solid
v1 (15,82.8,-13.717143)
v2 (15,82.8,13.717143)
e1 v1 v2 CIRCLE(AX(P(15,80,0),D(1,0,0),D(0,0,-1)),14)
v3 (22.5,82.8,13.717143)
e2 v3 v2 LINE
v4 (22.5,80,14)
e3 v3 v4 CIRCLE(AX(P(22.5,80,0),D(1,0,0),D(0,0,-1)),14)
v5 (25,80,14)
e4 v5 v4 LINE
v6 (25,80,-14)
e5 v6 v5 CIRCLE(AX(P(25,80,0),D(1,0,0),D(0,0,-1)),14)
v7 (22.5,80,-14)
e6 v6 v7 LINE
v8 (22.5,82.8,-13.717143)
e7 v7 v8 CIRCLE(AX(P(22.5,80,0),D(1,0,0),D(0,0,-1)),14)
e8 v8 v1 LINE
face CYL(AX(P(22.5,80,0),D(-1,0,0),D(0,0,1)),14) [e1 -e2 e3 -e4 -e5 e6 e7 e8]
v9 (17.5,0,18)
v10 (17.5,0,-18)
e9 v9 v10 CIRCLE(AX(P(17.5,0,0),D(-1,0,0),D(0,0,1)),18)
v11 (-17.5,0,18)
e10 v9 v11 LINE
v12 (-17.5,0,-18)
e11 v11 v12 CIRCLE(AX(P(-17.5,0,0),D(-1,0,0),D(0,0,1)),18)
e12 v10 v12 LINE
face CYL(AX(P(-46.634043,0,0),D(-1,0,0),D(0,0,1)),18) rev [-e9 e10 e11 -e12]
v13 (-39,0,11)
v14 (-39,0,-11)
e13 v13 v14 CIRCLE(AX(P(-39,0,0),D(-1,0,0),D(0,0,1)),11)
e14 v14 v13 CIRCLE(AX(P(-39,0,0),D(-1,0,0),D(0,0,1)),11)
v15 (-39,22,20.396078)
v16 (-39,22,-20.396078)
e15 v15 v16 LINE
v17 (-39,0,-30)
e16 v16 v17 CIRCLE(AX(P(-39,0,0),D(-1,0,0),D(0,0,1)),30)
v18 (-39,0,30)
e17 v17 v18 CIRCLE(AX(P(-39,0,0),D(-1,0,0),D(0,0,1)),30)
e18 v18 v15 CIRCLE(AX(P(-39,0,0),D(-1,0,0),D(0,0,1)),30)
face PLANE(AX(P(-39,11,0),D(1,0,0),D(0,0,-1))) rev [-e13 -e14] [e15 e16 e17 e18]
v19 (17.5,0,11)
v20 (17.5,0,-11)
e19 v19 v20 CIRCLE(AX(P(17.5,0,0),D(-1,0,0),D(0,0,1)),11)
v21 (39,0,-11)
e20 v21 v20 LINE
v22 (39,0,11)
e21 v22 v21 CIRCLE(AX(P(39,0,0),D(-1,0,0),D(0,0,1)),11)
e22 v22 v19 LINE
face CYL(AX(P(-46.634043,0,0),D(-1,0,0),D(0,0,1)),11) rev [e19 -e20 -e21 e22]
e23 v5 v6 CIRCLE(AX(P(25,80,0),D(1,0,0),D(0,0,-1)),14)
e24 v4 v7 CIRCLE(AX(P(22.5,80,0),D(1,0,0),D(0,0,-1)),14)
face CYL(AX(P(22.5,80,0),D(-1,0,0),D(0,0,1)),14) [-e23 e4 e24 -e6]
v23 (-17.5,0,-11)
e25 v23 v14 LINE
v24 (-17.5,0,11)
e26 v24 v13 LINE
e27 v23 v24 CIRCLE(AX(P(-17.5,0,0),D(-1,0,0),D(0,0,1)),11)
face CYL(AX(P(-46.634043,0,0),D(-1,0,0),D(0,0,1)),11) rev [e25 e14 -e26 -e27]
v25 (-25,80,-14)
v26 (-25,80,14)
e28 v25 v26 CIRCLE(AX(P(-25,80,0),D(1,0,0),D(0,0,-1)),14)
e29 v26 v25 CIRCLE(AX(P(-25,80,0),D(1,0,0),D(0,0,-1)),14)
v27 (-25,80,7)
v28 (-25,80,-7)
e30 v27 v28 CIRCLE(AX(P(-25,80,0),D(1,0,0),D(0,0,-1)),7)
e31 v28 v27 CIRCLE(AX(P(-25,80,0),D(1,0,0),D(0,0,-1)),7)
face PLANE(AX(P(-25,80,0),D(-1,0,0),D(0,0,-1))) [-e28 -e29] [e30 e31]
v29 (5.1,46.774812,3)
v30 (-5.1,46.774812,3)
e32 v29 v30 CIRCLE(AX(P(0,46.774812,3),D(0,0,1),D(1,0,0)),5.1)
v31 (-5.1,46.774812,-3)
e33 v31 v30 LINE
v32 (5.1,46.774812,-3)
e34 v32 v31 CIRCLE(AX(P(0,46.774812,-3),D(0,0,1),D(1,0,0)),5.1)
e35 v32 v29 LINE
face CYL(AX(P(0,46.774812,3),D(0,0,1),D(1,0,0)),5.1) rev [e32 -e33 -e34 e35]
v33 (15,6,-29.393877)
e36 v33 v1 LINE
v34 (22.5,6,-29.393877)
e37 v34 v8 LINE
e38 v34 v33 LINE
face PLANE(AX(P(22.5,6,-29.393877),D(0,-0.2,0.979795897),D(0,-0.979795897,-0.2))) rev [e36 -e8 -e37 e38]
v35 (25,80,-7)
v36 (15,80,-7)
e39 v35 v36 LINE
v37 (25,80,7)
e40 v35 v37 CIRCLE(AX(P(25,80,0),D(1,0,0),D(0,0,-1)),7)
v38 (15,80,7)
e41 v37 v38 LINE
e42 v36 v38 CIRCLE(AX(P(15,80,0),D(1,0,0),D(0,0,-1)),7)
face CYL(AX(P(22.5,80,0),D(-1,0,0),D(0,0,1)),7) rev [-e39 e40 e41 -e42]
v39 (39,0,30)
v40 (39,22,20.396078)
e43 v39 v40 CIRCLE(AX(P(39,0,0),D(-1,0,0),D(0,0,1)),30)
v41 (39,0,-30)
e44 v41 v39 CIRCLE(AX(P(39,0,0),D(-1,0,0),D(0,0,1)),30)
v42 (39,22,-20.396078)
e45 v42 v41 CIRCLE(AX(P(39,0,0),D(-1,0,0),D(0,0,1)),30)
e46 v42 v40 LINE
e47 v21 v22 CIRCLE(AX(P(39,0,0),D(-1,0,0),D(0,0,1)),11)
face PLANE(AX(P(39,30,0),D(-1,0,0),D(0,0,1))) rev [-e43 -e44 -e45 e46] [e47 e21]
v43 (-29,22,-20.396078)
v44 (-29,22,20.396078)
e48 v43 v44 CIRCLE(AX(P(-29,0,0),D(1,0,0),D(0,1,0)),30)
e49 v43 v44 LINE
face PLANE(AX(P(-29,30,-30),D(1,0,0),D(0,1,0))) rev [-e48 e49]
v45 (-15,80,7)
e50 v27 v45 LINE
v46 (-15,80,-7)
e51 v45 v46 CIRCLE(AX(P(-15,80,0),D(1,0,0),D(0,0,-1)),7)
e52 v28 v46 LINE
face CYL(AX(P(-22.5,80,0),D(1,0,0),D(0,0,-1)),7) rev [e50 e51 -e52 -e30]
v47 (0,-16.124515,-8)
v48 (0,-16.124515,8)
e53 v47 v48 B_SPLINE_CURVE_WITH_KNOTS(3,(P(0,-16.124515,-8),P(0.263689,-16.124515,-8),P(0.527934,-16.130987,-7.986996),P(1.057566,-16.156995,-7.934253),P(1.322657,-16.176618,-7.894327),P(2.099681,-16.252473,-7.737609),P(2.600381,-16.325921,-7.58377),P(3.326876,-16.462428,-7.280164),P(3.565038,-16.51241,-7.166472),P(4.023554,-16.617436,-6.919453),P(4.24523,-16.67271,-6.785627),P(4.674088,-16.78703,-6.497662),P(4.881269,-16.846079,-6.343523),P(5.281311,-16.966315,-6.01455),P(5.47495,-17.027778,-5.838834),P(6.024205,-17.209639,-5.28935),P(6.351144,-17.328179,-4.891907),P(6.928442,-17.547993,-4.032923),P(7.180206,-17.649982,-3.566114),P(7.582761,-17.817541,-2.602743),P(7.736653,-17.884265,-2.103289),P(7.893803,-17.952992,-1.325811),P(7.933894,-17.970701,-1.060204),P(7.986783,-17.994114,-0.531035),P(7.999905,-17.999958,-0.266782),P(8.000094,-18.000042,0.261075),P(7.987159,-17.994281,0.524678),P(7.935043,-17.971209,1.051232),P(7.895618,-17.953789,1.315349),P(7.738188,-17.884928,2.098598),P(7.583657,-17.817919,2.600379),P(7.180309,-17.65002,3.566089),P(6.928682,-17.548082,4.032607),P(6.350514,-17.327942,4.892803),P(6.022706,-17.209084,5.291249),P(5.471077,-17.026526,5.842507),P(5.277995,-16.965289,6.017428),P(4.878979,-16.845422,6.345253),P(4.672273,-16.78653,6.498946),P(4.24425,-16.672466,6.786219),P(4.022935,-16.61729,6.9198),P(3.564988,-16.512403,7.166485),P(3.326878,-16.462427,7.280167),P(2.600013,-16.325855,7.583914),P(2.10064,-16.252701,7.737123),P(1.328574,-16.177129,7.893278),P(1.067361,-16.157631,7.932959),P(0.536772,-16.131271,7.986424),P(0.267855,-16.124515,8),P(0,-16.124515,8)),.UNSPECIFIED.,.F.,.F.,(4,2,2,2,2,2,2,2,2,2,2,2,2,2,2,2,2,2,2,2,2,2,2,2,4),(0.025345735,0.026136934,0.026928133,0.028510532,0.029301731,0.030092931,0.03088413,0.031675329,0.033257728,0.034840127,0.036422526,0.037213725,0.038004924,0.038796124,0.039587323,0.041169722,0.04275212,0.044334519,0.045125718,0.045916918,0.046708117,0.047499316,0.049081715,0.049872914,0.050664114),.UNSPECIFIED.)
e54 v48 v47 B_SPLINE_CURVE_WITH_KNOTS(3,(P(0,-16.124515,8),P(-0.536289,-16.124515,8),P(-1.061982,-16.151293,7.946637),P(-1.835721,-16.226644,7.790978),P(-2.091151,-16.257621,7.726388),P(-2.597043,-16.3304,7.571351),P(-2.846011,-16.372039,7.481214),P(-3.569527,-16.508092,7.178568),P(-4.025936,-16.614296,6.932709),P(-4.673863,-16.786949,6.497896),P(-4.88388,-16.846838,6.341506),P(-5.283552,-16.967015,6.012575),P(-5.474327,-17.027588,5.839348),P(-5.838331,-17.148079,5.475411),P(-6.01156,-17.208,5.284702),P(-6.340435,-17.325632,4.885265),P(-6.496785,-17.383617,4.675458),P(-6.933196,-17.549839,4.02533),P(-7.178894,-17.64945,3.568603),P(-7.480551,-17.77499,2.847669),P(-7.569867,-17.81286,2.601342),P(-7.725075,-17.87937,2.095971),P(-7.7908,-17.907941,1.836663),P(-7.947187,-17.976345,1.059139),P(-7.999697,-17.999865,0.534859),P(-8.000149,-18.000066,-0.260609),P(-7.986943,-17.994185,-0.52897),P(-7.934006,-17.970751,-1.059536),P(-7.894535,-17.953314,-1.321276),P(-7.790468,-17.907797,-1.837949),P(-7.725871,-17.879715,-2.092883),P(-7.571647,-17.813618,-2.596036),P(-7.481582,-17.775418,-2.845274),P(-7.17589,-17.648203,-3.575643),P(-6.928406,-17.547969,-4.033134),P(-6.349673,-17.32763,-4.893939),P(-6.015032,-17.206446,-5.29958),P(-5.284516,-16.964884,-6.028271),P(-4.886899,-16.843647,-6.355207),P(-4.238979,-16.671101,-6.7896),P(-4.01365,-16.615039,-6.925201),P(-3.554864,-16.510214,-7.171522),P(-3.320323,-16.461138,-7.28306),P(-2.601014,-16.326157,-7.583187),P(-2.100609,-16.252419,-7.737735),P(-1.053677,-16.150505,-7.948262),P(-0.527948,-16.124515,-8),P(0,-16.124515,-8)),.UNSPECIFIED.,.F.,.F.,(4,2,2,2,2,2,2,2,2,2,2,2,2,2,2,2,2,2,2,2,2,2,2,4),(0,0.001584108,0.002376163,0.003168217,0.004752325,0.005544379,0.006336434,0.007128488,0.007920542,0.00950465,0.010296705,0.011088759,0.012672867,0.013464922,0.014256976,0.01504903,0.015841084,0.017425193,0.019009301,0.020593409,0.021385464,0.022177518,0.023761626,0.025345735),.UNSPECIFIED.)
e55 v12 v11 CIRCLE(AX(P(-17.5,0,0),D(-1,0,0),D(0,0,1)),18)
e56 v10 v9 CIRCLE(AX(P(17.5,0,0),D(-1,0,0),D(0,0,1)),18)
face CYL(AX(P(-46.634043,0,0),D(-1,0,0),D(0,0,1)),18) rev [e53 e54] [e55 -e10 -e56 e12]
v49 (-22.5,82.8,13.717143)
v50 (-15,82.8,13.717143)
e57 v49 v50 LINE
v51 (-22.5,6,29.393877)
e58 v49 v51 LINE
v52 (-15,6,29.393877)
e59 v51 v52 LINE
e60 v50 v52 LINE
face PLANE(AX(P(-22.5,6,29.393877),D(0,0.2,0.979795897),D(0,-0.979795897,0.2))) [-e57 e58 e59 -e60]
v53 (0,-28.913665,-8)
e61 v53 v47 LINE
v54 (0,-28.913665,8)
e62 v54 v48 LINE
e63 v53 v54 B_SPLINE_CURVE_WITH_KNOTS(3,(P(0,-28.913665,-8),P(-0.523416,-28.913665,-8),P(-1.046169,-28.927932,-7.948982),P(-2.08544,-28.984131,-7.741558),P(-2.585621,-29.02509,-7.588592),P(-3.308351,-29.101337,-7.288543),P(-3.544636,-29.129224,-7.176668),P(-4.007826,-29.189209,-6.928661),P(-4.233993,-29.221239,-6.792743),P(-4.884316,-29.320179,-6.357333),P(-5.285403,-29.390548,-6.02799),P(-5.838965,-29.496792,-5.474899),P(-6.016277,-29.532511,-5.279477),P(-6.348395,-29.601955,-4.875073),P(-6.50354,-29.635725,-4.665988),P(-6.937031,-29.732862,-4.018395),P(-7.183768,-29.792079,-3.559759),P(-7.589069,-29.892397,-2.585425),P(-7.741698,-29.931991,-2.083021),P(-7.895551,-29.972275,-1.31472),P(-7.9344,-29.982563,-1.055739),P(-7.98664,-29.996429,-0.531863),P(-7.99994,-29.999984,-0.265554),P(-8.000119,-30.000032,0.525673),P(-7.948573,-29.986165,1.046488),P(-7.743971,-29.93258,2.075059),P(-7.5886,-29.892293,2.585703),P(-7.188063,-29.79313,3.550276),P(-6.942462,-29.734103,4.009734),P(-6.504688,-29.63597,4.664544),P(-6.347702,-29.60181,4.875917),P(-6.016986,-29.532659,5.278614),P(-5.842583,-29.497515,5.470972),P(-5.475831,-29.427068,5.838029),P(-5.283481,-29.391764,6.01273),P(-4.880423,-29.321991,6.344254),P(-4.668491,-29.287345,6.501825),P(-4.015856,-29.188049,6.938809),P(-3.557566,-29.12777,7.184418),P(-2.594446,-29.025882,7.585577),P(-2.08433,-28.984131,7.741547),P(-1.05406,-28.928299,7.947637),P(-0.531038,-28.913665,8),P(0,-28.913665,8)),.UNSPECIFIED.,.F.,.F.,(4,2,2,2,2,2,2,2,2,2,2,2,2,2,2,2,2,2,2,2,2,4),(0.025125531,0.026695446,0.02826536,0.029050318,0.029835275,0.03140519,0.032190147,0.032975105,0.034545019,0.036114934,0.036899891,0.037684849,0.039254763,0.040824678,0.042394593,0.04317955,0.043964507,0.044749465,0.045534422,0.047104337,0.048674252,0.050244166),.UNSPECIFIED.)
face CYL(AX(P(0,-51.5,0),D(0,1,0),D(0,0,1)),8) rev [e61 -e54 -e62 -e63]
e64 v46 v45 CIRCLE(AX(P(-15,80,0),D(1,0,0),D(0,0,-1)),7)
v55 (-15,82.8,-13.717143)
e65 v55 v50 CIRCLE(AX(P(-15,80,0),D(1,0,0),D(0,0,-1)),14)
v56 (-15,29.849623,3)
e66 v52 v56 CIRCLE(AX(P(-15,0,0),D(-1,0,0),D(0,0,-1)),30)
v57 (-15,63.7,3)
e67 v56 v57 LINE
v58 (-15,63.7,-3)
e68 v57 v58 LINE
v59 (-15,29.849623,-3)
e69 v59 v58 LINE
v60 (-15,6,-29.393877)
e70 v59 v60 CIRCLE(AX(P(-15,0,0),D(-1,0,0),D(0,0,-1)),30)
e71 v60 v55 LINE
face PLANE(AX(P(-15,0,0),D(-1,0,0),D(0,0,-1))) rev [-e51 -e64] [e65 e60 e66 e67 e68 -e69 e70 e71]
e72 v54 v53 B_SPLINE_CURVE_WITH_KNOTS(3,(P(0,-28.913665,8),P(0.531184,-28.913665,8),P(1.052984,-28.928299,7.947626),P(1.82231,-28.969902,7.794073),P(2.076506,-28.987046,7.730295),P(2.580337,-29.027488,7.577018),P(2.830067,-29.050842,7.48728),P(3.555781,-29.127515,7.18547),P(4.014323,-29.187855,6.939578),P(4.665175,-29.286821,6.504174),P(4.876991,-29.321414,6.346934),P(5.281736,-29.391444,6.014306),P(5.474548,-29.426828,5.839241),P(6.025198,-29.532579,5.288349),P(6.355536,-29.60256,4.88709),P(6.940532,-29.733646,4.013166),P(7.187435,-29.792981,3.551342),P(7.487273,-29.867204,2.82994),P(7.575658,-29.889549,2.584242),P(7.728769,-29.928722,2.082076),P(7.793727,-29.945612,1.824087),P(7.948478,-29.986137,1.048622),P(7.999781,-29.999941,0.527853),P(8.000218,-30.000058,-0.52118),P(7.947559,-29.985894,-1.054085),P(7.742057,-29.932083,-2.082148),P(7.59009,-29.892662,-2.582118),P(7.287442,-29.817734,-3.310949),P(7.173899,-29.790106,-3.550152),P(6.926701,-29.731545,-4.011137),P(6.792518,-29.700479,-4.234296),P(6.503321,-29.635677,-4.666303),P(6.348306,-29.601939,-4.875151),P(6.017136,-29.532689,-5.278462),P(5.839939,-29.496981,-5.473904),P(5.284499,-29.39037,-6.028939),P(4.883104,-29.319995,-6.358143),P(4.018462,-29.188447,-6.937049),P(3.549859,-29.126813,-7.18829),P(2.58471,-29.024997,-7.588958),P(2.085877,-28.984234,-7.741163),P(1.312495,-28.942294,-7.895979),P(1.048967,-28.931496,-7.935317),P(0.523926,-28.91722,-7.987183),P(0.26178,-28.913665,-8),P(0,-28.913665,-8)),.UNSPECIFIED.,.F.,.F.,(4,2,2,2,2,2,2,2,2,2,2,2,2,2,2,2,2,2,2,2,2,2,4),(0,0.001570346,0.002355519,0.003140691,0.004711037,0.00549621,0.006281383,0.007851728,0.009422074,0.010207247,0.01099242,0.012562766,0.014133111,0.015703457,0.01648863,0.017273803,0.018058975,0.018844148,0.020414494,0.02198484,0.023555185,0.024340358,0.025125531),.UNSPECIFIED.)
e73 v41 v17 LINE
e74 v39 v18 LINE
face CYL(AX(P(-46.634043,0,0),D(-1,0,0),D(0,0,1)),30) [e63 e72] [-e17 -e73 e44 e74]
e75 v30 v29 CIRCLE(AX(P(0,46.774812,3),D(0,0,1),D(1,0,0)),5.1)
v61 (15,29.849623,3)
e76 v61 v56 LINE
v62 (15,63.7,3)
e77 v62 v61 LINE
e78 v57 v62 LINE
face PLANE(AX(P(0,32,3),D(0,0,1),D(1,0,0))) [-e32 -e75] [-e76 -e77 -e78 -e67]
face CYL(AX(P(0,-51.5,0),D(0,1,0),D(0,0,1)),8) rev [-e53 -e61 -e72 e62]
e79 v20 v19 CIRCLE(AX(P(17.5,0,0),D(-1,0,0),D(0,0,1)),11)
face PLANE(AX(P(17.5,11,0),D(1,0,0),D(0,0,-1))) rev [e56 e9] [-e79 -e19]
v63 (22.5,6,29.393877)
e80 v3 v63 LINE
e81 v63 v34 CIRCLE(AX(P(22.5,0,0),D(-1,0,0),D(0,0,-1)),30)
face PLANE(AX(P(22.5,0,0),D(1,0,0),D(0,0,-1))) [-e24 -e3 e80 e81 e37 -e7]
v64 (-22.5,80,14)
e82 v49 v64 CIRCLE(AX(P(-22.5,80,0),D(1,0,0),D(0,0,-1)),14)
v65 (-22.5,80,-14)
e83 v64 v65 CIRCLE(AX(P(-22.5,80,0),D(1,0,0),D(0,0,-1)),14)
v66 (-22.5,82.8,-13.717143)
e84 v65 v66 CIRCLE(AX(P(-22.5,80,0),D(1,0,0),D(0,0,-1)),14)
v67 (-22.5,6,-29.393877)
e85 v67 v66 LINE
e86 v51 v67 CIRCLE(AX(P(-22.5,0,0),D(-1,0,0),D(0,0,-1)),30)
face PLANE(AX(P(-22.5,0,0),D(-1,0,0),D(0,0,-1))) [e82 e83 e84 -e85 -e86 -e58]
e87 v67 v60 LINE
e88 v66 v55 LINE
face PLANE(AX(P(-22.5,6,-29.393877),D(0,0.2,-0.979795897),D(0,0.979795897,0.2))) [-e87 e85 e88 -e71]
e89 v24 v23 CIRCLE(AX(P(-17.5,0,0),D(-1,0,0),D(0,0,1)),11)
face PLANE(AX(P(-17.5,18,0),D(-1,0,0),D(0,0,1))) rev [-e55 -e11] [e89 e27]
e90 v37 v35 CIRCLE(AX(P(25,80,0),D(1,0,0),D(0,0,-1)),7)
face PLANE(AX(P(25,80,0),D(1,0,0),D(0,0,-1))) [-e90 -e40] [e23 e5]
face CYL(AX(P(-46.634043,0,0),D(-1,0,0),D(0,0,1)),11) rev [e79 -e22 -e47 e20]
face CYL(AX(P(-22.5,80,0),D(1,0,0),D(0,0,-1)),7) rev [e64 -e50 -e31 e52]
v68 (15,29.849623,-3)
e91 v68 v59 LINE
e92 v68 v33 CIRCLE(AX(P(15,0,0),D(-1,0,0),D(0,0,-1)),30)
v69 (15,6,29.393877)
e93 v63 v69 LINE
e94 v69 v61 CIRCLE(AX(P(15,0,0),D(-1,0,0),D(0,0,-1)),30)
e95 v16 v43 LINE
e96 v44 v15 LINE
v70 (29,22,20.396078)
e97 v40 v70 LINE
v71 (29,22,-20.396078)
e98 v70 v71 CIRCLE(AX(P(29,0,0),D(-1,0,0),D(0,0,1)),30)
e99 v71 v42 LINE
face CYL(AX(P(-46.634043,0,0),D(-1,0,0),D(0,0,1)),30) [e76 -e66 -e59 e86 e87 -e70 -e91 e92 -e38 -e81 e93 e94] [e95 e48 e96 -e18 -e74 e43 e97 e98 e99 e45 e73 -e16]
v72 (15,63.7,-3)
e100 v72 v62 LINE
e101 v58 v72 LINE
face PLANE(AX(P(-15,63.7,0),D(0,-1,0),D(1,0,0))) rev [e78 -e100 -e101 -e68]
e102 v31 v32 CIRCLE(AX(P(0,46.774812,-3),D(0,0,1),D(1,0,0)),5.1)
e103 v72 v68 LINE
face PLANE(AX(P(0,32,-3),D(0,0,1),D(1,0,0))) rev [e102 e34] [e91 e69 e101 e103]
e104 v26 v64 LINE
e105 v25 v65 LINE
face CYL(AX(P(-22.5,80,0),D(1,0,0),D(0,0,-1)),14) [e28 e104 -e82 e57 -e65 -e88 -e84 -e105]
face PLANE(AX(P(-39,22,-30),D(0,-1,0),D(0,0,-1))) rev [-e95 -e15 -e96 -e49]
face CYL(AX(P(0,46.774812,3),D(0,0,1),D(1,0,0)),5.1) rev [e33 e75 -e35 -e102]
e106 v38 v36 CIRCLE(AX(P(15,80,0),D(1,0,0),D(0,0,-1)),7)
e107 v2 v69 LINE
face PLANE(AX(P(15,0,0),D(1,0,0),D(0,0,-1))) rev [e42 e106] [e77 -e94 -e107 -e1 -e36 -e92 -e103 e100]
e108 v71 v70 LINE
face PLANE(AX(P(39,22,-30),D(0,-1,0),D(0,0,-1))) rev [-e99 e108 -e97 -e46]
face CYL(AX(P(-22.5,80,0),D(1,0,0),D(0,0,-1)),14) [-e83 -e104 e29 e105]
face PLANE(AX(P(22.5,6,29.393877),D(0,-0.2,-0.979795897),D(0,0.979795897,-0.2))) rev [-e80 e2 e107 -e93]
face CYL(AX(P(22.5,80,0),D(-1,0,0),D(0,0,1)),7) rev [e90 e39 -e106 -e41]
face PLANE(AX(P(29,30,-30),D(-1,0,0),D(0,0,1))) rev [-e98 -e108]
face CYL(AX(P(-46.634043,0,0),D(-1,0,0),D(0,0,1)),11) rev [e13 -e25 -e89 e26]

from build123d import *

# Parameters (mm, degrees)
EYE_START                  = 22.5
EYE_LUG_SKETCH_R           = 7
EYE_LUG_DEPTH              = 7.5
EYE_START_2                = 2.5
EYE_BOSS_SKETCH_R          = 14
EYE_BOSS_SKETCH_R_2        = 7
EYE_BOSS_28_DEPTH          = 2.5
WEB_RIB_6MM_REACH          = 108.099
WEB_RIB_SKETCH_WALL_W      = 244.198020726
WEB_RIB_SKETCH_WALL_H      = 6
CROSS_BORE_SKETCH_R        = 8
CROSS_BORE_16_DEPTH        = 51.5
TAPPED_HOLE_M12_D          = 10.2
BARREL_SLOT_CUT_DEPTH      = 107.099010428
BARREL_SLOT_CUT_DEPTH_BACK = 107.099010428
BARREL_SLOT_SKETCH_W       = 10
BARREL_SLOT_SKETCH_H       = 8


with BuildPart() as part:
    # Barrel Profile Sketch → Cylinder Barrel (revolve)
    with BuildSketch(Plane.XY, mode=Mode.PRIVATE) as cylinder_barrel_sk:
        Polygon((-39, 11), (-39, 30), (39, 30), (39, 11), (17.5, 11), (17.5, 18), (-17.5, 18), (-17.5, 11), align=None)
    revolve(cylinder_barrel_sk.sketch.rotate(Axis((-46.634042553, 0, 0), (1, 0, 0)), 90), axis=Axis((-46.634042553, 0, 0), (1, 0, 0)))

    # Eye Lug Sketch → Eye Lug (add)
    with BuildSketch(Plane(origin=(0, 0, 0), x_dir=(0, 0, -1), z_dir=(1, 0, 0)).offset(EYE_START)):
        with BuildLine():
            Line((-29.393876913, 6), (-13.71714256, 82.8))
            ThreePointArc((-13.71714256, 82.8), (0, 94), (13.71714256, 82.8))
            Line((13.71714256, 82.8), (29.393876913, 6))
            ThreePointArc((29.393876913, 6), (0, 30), (-29.393876913, 6))
        make_face()
        with Locations((0, 80)):
            Circle(EYE_LUG_SKETCH_R, mode=Mode.SUBTRACT)
    eye_lug = extrude(amount=-EYE_LUG_DEPTH)

    # Eye Boss Sketch → Eye Boss Ø28 (add)
    with BuildSketch(Plane(origin=(22.5, 0, 0), x_dir=(0, 0, -1), z_dir=(1, 0, 0)).offset(EYE_START_2)):
        with Locations(Location((0, 80, 0), (0, 0, 168.463040967))):
            Circle(EYE_BOSS_SKETCH_R)
        with Locations((0, 80)):
            Circle(EYE_BOSS_SKETCH_R_2, mode=Mode.SUBTRACT)
    eye_boss_28 = extrude(amount=-EYE_BOSS_28_DEPTH)

    # Mirrored Eye Lug: Eye Lug, Eye Boss Ø28 across plane
    add(eye_lug.mirror(Plane(origin=(0, 0, 0), x_dir=(0, 0, 1), z_dir=(1, 0, 0))))
    add(eye_boss_28.mirror(Plane(origin=(0, 0, 0), x_dir=(0, 0, 1), z_dir=(1, 0, 0))))

    # Web Rib Sketch wall → Web Rib 6mm (add, up to next)
    with BuildSketch(Plane(origin=(0, 63.7, 0), x_dir=(1, 0, 0), z_dir=(0, 1, 0)), mode=Mode.PRIVATE) as web_rib_6mm_sk1:
        Rectangle(WEB_RIB_SKETCH_WALL_W, WEB_RIB_SKETCH_WALL_H)
    web_rib_6mm_tool1 = extrude(web_rib_6mm_sk1.sketch, amount=-WEB_RIB_6MM_REACH, mode=Mode.PRIVATE) - part.part
    add(web_rib_6mm_tool1.solids().sort_by_distance((0, 63.7, 0))[0])

    # Cross Bore Sketch → Cross Bore Ø16 (cut)
    with BuildSketch(Plane(origin=(0, 0, 0), x_dir=(1, 0, 0), z_dir=(0, 1, 0))):
        with Locations(Location((0, 0, 0), (0, 0, 270))):
            Circle(CROSS_BORE_SKETCH_R)
    extrude(amount=-CROSS_BORE_16_DEPTH, mode=Mode.SUBTRACT)

    # Tapped Hole M12 (through all)
    with Locations(Plane(origin=(0, 46.774811557, 3), x_dir=(1, 0, 0), z_dir=(0, 0, 1))):
        with Locations((0, 0)):
            Hole(TAPPED_HOLE_M12_D / 2)

    # Barrel Slot Sketch → Barrel Slot Cut (cut, two sides: drawn at the far end of the back side and taken through both)
    with BuildSketch(Plane.XY.offset(-BARREL_SLOT_CUT_DEPTH_BACK)):
        with Locations((-34, 26)):
            Rectangle(BARREL_SLOT_SKETCH_W, BARREL_SLOT_SKETCH_H)
        with Locations((34, 26)):
            Rectangle(BARREL_SLOT_SKETCH_W, BARREL_SLOT_SKETCH_H)
    extrude(amount=BARREL_SLOT_CUT_DEPTH + BARREL_SLOT_CUT_DEPTH_BACK, mode=Mode.SUBTRACT)


solid = part.part
